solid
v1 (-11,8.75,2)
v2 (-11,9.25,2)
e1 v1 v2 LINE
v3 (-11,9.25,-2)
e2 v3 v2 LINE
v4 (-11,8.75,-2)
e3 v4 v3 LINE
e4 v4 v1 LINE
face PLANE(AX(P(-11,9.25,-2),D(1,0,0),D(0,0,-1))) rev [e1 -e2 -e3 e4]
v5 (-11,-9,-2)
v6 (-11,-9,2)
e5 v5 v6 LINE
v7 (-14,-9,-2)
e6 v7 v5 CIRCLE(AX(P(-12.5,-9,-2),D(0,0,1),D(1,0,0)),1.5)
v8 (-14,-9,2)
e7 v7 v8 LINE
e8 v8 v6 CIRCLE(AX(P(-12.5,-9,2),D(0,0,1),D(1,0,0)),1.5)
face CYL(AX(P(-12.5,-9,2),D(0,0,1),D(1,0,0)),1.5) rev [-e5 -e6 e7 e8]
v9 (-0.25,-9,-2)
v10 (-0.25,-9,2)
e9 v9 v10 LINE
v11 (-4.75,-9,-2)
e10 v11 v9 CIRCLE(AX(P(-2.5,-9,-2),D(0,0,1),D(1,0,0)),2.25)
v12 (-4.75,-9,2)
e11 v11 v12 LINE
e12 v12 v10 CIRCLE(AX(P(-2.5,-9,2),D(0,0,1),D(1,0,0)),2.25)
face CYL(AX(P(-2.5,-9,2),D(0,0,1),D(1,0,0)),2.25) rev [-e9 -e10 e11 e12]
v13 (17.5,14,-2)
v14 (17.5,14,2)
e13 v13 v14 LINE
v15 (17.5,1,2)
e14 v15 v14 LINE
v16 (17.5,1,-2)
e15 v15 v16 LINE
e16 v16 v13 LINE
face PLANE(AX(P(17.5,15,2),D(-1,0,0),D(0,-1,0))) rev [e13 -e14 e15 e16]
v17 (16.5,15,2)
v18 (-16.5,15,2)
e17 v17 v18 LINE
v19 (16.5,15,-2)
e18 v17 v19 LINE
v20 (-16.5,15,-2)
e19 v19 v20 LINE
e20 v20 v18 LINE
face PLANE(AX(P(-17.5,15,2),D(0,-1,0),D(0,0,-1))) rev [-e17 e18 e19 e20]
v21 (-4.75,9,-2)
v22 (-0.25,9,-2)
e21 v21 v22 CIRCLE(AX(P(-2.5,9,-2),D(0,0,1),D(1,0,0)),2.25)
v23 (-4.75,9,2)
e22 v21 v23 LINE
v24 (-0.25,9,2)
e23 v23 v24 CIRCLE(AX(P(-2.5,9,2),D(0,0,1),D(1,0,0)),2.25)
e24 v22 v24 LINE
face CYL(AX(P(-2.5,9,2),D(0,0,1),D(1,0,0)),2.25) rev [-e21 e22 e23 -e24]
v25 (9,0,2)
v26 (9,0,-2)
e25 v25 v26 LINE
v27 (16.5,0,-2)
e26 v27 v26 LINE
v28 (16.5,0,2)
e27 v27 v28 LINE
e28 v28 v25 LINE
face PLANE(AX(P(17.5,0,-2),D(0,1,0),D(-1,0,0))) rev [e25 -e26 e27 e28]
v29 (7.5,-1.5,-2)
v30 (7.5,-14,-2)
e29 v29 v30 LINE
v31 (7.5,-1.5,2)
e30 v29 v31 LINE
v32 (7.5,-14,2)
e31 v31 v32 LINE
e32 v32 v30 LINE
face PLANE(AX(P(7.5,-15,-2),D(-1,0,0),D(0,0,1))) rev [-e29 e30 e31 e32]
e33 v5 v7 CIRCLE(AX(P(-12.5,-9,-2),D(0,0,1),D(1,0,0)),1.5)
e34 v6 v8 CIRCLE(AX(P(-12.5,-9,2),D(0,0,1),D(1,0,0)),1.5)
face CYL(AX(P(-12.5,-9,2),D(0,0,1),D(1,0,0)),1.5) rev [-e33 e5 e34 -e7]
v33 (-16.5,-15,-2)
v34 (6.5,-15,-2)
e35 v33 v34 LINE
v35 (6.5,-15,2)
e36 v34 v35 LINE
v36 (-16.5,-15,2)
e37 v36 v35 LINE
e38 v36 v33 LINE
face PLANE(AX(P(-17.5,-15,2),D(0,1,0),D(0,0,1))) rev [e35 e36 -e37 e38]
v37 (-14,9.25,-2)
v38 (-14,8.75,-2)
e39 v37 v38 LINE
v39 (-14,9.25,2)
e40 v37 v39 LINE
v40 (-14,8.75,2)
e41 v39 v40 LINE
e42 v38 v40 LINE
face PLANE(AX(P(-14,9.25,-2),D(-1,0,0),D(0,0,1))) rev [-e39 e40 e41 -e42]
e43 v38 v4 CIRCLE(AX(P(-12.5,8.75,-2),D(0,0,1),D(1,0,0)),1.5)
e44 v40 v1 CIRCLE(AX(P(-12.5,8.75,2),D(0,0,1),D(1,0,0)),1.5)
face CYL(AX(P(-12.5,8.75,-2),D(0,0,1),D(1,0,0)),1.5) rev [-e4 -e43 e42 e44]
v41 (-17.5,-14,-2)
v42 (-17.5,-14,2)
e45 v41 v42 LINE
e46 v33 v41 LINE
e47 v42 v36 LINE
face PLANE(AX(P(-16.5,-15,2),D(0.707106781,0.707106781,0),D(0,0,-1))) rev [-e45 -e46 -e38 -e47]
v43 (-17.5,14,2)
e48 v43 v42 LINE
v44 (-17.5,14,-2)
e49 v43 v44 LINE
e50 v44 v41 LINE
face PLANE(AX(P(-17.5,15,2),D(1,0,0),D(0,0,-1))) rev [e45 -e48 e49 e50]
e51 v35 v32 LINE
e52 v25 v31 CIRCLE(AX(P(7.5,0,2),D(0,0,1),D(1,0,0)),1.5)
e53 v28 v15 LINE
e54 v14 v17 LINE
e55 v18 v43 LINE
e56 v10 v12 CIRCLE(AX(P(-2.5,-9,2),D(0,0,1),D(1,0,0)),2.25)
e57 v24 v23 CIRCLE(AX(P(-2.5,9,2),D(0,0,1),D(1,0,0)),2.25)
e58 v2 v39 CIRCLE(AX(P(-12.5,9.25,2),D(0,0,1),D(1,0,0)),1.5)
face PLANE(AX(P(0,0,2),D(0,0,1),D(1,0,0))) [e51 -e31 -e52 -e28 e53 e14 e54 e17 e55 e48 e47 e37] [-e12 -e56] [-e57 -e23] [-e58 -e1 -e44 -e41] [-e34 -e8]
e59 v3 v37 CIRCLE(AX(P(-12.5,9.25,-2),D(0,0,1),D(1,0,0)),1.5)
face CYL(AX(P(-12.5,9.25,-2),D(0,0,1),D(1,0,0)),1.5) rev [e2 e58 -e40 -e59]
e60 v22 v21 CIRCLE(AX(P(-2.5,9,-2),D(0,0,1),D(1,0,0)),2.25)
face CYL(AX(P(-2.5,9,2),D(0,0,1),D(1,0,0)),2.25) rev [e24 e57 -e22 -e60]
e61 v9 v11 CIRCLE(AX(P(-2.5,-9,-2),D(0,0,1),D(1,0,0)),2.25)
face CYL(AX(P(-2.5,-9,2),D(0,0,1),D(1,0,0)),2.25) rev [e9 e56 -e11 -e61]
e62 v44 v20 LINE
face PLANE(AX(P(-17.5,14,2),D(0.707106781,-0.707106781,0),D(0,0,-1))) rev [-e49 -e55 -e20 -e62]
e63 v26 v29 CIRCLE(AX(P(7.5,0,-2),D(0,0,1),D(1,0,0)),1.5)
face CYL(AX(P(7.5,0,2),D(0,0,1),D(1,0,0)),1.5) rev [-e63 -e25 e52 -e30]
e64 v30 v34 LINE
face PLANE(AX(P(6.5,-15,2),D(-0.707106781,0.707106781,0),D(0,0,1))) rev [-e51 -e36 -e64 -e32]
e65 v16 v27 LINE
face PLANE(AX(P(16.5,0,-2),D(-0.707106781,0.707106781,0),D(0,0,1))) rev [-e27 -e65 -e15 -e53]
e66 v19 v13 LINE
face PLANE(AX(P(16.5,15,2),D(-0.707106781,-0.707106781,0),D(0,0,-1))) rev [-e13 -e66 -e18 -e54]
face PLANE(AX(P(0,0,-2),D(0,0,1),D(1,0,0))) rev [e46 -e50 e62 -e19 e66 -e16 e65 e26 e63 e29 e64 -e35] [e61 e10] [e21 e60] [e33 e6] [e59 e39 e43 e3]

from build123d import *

# Parameters (mm, degrees)
SKETCH1_W                  = 35
SKETCH1_H                  = 30
BOSS_EXTRUDE1_DEPTH        = 2
SKETCH2_W                  = 10
SKETCH2_H                  = 15
CUT_EXTRUDE1_DEPTH         = 24.393375131
F_3_0_3_DIAMETER_HOLE2_D   = 3
F_3_0_3_DIAMETER_HOLE1_D   = 3
F_4_5_4_5_DIAMETER_HOLE1_D = 4.5
CHAMFER1_SIZE              = 1
CUT_EXTRUDE2_DEPTH         = 24.393375131


with BuildPart() as part:
    # Sketch1 → Boss-Extrude1 (new, symmetric)
    with BuildSketch(Plane.XY):
        Rectangle(SKETCH1_W, SKETCH1_H)
    extrude(amount=BOSS_EXTRUDE1_DEPTH, both=True)

    # Sketch2 → Cut-Extrude1 (cut, through all)
    with BuildSketch(Plane.XY.offset(2)):
        with Locations((12.5, -7.5)):
            Rectangle(SKETCH2_W, SKETCH2_H)
    extrude(amount=-CUT_EXTRUDE1_DEPTH, mode=Mode.SUBTRACT)

    # Ø3.0 (3) Diameter Hole2 (through all)
    with Locations(Plane.XY.offset(2)):
        with Locations((7.5, 0)):
            Hole(F_3_0_3_DIAMETER_HOLE2_D / 2)

    # Ø3.0 (3) Diameter Hole1 (through all)
    with Locations(Plane.XY.offset(2)):
        with Locations((-12.5, 9), (-12.5, -9)):
            Hole(F_3_0_3_DIAMETER_HOLE1_D / 2)

    # Ø4.5 (4.5) Diameter Hole1 (through all)
    with Locations(Plane.XY.offset(2)):
        with Locations((-2.5, 9), (-2.5, -9)):
            Hole(F_4_5_4_5_DIAMETER_HOLE1_D / 2)

    # Chamfer1
    chamfer1_edges = [part.edges().sort_by_distance(p)[0] for p in [
        (17.5, 0, 0),
        (7.5, -15, 0),
        (-17.5, -15, 0),
        (-17.5, 15, 0),
        (17.5, 15, 0),
    ]]
    chamfer(chamfer1_edges, length=CHAMFER1_SIZE)

    # Sketch9 → Cut-Extrude2 (cut, through all)
    with BuildSketch(Plane.XY.offset(2)):
        with BuildLine():
            Line((-11, 9.25), (-11, 8.75))
            ThreePointArc((-11, 8.75), (-12.5, 7.25), (-14, 8.75))
            Line((-14, 8.75), (-14, 9.25))
            ThreePointArc((-14, 9.25), (-12.5, 10.75), (-11, 9.25))
        make_face()
    extrude(amount=-CUT_EXTRUDE2_DEPTH, mode=Mode.SUBTRACT)


solid = part.part
